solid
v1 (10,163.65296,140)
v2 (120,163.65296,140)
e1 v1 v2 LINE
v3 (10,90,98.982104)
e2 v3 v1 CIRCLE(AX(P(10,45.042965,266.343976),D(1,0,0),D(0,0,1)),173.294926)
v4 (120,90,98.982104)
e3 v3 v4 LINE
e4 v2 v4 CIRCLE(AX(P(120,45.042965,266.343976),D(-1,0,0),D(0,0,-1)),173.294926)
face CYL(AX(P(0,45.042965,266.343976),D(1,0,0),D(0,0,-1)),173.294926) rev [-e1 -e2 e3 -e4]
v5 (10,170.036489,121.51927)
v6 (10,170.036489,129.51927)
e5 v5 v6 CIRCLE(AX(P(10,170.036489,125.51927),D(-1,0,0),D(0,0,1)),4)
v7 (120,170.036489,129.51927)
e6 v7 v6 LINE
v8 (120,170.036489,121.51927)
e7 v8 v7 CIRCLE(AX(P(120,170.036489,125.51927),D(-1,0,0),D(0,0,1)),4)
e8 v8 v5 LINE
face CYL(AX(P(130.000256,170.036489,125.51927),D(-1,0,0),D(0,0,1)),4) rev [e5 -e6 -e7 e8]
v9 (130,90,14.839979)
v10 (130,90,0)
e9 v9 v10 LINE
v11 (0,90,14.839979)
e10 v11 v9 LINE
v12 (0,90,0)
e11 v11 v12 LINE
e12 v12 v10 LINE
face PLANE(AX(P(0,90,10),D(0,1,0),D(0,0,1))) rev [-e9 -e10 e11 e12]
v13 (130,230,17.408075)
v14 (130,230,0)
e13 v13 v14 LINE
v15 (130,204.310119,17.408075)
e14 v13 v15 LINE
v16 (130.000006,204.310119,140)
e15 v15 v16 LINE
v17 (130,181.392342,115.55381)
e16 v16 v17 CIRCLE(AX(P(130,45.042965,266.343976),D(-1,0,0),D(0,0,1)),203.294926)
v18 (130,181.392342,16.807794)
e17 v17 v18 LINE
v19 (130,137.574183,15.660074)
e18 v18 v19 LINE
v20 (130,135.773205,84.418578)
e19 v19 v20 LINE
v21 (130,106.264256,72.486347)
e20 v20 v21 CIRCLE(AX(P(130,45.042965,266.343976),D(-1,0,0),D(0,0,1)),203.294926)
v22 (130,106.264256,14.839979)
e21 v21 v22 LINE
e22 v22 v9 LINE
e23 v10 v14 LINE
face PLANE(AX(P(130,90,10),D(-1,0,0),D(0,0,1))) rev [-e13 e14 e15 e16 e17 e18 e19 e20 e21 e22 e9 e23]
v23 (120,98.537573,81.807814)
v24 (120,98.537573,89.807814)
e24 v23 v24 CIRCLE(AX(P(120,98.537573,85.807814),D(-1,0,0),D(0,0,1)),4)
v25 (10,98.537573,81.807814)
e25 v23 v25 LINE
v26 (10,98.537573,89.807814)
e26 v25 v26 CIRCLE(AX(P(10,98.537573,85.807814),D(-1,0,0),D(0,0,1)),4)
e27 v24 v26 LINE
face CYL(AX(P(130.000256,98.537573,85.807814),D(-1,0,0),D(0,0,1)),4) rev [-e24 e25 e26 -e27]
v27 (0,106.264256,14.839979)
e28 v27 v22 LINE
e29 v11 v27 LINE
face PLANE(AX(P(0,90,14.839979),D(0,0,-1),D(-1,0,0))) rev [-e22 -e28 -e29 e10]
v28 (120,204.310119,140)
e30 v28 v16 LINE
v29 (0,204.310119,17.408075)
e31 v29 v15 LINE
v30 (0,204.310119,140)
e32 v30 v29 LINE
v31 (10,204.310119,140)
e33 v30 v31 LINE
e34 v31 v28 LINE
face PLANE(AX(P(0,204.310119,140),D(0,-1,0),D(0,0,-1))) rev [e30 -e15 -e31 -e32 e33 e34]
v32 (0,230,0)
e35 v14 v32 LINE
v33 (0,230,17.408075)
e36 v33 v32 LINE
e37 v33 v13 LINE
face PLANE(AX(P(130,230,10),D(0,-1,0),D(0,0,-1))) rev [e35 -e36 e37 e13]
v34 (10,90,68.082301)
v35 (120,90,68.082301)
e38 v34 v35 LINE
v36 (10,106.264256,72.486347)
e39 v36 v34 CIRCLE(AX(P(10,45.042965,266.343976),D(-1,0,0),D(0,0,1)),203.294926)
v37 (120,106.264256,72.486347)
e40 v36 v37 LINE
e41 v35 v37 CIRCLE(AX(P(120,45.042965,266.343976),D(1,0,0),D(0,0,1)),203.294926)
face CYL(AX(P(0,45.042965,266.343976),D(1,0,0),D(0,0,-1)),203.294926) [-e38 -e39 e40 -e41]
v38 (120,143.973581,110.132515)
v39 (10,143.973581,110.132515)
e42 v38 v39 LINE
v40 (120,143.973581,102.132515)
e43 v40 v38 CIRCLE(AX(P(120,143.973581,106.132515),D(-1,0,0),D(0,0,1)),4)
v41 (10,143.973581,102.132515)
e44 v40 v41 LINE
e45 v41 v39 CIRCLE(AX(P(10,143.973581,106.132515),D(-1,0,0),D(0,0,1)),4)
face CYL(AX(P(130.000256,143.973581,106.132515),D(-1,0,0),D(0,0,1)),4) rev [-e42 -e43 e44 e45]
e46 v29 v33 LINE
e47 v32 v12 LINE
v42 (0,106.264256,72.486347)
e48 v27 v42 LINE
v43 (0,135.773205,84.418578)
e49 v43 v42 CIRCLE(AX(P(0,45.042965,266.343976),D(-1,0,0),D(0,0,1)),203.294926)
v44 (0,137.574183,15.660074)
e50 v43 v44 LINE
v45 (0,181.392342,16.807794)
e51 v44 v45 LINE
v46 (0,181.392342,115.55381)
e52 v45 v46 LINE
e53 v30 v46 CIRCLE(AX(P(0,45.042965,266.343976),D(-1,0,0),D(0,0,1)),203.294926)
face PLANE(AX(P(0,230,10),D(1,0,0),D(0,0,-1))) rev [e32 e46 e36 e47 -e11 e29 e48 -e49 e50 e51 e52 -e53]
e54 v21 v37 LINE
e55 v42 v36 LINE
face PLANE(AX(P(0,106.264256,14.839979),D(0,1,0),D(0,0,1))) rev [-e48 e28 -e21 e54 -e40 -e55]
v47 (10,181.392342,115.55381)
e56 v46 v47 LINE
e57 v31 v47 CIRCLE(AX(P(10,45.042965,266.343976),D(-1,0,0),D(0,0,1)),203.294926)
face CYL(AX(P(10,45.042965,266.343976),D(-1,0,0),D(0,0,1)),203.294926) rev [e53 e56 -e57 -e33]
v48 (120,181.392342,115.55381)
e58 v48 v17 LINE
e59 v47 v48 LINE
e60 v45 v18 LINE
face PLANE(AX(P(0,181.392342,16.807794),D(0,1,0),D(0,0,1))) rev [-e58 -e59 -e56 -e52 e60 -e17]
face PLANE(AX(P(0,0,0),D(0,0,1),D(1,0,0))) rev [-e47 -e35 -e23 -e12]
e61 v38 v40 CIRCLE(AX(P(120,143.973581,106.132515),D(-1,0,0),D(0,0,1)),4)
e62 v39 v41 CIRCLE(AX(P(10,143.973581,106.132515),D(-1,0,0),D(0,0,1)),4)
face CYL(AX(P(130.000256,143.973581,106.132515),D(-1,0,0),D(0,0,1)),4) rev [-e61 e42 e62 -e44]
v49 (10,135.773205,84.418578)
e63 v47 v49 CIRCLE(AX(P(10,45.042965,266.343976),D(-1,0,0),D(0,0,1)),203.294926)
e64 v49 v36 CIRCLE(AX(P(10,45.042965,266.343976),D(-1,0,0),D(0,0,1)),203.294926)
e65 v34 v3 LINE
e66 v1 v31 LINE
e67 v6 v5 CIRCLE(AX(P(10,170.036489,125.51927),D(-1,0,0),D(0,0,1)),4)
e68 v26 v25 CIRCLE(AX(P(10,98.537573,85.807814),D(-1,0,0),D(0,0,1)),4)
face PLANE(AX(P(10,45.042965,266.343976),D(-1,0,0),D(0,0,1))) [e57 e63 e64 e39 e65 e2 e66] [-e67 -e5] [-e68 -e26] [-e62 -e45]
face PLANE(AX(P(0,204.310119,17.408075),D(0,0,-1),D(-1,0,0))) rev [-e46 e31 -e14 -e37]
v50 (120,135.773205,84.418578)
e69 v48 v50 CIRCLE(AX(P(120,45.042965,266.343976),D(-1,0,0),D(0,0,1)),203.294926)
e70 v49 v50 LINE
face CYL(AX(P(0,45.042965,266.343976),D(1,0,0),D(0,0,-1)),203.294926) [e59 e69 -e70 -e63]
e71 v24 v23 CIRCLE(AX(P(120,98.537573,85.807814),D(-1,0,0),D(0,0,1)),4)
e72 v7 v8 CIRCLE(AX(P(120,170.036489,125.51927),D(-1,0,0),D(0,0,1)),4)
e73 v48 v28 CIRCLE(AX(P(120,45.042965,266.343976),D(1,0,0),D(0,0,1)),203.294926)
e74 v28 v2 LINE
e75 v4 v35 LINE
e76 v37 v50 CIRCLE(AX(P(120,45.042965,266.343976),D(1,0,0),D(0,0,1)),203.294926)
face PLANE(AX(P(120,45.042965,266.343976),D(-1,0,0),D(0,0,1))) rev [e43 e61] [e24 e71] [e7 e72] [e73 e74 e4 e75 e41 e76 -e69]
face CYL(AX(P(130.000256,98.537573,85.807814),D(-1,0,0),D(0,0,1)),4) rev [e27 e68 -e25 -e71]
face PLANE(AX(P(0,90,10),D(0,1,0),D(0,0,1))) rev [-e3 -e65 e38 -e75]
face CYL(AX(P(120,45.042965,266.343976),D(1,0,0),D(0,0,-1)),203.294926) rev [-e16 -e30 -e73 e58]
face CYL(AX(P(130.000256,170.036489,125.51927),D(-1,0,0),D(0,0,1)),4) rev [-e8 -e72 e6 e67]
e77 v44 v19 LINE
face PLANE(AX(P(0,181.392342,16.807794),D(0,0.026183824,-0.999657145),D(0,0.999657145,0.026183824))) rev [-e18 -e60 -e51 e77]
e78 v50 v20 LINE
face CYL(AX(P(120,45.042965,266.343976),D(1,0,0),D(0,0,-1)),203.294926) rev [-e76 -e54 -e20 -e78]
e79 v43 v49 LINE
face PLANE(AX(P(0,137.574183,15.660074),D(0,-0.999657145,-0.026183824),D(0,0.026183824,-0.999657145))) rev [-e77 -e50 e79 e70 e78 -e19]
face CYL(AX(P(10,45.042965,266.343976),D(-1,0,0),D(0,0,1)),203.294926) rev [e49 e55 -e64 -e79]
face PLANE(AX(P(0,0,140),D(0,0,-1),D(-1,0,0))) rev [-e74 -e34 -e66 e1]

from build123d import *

# Parameters (mm, degrees)
SKETCH1_W               = 130
SKETCH1_H               = 140
BOSS_EXTRUDE1_DEPTH     = 10
SKETCH14_W              = 130
SKETCH14_H              = 140
BOSS_EXTRUDE2_DEPTH     = 130
CUT_EXTRUDE2_DEPTH      = 299.998327755
CUT_EXTRUDE2_DEPTH_BACK = 299.998327755
SKETCH15_W              = 122.59192481
SKETCH15_H              = 25.689880701
CUT_EXTRUDE4_DEPTH      = 299.998327755
CUT_EXTRUDE4_DEPTH_BACK = 10
CUT_EXTRUDE5_DEPTH      = 10
CUT_EXTRUDE6_DEPTH      = 295.78805946
CUT_EXTRUDE6_DEPTH_BACK = 295.78805946
SKETCH19_R              = 4


with BuildPart() as part:
    # Sketch1 → Boss-Extrude1 (new body)
    with BuildSketch(Plane.XY):
        with Locations((65, 160)):
            Rectangle(SKETCH1_W, SKETCH1_H)
    extrude(amount=BOSS_EXTRUDE1_DEPTH)

    # Sketch14 → Boss-Extrude2 (add)
    with BuildSketch(Plane.XY.offset(10)):
        with Locations((65, 160)):
            Rectangle(SKETCH14_W, SKETCH14_H)
    extrude(amount=BOSS_EXTRUDE2_DEPTH)

    # Sketch15 → Cut-Extrude2 (cut, two sides: drawn at the far end of the back side and taken through both)
    with BuildSketch(Plane(origin=(130, 0, 0), x_dir=(0, 0, -1), z_dir=(1, 0, 0)).offset(-CUT_EXTRUDE2_DEPTH_BACK)):
        with BuildLine():
            Line((-140, 90), (-140, 163.652960017))
            ThreePointArc((-140, 163.652960017), (-114.94393992, 129.358801446), (-98.982103949, 90))
            Line((-98.982103949, 90), (-140, 90))
        make_face()
        with BuildLine():
            Line((-68.08230106, 90), (-14.839979069, 90))
            Line((-14.839979069, 90), (-14.839979069, 106.264255909))
            Line((-14.839979069, 106.264255909), (-72.486347105, 106.264255909))
            ThreePointArc((-72.486347105, 106.264255909), (-70.115745067, 98.177775893), (-68.08230106, 90))
        make_face()
        with Locations((-78.704037595, 217.15505965)):
            Rectangle(SKETCH15_W, SKETCH15_H)
        with BuildLine():
            Line((-16.807794328, 181.392341835), (-15.660073853, 137.574182571))
            Line((-15.660073853, 137.574182571), (-84.418578186, 135.773204516))
            ThreePointArc((-84.418578186, 135.773204516), (-98.429747838, 159.645053575), (-115.553810025, 181.392341835))
            Line((-115.553810025, 181.392341835), (-16.807794328, 181.392341835))
        make_face()
    extrude(amount=CUT_EXTRUDE2_DEPTH + CUT_EXTRUDE2_DEPTH_BACK, mode=Mode.SUBTRACT)

    # Sketch17 → Cut-Extrude4 (cut, two sides: drawn at the far end of the back side and taken through both)
    with BuildSketch(Plane(origin=(130, 0, 0), x_dir=(0, 0, -1), z_dir=(1, 0, 0)).offset(-CUT_EXTRUDE4_DEPTH_BACK)):
        with BuildLine():
            Line((-140, 204.310119299), (-140, 163.652960017))
            ThreePointArc((-140, 163.652960017), (-114.94393992, 129.358801446), (-98.982103949, 90))
            Line((-98.982103949, 90), (-68.08230106, 90))
            ThreePointArc((-68.08230106, 90), (-70.115745067, 98.177775893), (-72.486347105, 106.264255909))
            ThreePointArc((-72.486347105, 106.264255909), (-98.905883629, 160.339590918), (-140, 204.310119299))
        make_face()
    extrude(amount=CUT_EXTRUDE4_DEPTH + CUT_EXTRUDE4_DEPTH_BACK, mode=Mode.SUBTRACT)

    # Sketch18 → Cut-Extrude5 (cut)
    with BuildSketch(Plane.ZY):
        with BuildLine():
            Line((98.982103949, 90), (68.08230106, 90))
            ThreePointArc((68.08230106, 90), (94.271584258, 153.301538458), (140, 204.310119299))
            Line((140, 204.310119299), (140, 163.652960017))
            ThreePointArc((140, 163.652960017), (114.94393992, 129.358801446), (98.982103949, 90))
        make_face()
    extrude(amount=-CUT_EXTRUDE5_DEPTH, mode=Mode.SUBTRACT)

    # Sketch19 → Cut-Extrude6 (cut, two sides: drawn at the far end of the back side and taken through both)
    with BuildSketch(Plane.ZY.offset(-10).offset(-CUT_EXTRUDE6_DEPTH_BACK)):
        with Locations((85.807813583, 98.537572545)):
            Circle(SKETCH19_R)
        with Locations((106.132515119, 143.973580916)):
            Circle(SKETCH19_R)
        with Locations((125.519269901, 170.036489259)):
            Circle(SKETCH19_R)
    extrude(amount=CUT_EXTRUDE6_DEPTH + CUT_EXTRUDE6_DEPTH_BACK, mode=Mode.SUBTRACT)


solid = part.part
